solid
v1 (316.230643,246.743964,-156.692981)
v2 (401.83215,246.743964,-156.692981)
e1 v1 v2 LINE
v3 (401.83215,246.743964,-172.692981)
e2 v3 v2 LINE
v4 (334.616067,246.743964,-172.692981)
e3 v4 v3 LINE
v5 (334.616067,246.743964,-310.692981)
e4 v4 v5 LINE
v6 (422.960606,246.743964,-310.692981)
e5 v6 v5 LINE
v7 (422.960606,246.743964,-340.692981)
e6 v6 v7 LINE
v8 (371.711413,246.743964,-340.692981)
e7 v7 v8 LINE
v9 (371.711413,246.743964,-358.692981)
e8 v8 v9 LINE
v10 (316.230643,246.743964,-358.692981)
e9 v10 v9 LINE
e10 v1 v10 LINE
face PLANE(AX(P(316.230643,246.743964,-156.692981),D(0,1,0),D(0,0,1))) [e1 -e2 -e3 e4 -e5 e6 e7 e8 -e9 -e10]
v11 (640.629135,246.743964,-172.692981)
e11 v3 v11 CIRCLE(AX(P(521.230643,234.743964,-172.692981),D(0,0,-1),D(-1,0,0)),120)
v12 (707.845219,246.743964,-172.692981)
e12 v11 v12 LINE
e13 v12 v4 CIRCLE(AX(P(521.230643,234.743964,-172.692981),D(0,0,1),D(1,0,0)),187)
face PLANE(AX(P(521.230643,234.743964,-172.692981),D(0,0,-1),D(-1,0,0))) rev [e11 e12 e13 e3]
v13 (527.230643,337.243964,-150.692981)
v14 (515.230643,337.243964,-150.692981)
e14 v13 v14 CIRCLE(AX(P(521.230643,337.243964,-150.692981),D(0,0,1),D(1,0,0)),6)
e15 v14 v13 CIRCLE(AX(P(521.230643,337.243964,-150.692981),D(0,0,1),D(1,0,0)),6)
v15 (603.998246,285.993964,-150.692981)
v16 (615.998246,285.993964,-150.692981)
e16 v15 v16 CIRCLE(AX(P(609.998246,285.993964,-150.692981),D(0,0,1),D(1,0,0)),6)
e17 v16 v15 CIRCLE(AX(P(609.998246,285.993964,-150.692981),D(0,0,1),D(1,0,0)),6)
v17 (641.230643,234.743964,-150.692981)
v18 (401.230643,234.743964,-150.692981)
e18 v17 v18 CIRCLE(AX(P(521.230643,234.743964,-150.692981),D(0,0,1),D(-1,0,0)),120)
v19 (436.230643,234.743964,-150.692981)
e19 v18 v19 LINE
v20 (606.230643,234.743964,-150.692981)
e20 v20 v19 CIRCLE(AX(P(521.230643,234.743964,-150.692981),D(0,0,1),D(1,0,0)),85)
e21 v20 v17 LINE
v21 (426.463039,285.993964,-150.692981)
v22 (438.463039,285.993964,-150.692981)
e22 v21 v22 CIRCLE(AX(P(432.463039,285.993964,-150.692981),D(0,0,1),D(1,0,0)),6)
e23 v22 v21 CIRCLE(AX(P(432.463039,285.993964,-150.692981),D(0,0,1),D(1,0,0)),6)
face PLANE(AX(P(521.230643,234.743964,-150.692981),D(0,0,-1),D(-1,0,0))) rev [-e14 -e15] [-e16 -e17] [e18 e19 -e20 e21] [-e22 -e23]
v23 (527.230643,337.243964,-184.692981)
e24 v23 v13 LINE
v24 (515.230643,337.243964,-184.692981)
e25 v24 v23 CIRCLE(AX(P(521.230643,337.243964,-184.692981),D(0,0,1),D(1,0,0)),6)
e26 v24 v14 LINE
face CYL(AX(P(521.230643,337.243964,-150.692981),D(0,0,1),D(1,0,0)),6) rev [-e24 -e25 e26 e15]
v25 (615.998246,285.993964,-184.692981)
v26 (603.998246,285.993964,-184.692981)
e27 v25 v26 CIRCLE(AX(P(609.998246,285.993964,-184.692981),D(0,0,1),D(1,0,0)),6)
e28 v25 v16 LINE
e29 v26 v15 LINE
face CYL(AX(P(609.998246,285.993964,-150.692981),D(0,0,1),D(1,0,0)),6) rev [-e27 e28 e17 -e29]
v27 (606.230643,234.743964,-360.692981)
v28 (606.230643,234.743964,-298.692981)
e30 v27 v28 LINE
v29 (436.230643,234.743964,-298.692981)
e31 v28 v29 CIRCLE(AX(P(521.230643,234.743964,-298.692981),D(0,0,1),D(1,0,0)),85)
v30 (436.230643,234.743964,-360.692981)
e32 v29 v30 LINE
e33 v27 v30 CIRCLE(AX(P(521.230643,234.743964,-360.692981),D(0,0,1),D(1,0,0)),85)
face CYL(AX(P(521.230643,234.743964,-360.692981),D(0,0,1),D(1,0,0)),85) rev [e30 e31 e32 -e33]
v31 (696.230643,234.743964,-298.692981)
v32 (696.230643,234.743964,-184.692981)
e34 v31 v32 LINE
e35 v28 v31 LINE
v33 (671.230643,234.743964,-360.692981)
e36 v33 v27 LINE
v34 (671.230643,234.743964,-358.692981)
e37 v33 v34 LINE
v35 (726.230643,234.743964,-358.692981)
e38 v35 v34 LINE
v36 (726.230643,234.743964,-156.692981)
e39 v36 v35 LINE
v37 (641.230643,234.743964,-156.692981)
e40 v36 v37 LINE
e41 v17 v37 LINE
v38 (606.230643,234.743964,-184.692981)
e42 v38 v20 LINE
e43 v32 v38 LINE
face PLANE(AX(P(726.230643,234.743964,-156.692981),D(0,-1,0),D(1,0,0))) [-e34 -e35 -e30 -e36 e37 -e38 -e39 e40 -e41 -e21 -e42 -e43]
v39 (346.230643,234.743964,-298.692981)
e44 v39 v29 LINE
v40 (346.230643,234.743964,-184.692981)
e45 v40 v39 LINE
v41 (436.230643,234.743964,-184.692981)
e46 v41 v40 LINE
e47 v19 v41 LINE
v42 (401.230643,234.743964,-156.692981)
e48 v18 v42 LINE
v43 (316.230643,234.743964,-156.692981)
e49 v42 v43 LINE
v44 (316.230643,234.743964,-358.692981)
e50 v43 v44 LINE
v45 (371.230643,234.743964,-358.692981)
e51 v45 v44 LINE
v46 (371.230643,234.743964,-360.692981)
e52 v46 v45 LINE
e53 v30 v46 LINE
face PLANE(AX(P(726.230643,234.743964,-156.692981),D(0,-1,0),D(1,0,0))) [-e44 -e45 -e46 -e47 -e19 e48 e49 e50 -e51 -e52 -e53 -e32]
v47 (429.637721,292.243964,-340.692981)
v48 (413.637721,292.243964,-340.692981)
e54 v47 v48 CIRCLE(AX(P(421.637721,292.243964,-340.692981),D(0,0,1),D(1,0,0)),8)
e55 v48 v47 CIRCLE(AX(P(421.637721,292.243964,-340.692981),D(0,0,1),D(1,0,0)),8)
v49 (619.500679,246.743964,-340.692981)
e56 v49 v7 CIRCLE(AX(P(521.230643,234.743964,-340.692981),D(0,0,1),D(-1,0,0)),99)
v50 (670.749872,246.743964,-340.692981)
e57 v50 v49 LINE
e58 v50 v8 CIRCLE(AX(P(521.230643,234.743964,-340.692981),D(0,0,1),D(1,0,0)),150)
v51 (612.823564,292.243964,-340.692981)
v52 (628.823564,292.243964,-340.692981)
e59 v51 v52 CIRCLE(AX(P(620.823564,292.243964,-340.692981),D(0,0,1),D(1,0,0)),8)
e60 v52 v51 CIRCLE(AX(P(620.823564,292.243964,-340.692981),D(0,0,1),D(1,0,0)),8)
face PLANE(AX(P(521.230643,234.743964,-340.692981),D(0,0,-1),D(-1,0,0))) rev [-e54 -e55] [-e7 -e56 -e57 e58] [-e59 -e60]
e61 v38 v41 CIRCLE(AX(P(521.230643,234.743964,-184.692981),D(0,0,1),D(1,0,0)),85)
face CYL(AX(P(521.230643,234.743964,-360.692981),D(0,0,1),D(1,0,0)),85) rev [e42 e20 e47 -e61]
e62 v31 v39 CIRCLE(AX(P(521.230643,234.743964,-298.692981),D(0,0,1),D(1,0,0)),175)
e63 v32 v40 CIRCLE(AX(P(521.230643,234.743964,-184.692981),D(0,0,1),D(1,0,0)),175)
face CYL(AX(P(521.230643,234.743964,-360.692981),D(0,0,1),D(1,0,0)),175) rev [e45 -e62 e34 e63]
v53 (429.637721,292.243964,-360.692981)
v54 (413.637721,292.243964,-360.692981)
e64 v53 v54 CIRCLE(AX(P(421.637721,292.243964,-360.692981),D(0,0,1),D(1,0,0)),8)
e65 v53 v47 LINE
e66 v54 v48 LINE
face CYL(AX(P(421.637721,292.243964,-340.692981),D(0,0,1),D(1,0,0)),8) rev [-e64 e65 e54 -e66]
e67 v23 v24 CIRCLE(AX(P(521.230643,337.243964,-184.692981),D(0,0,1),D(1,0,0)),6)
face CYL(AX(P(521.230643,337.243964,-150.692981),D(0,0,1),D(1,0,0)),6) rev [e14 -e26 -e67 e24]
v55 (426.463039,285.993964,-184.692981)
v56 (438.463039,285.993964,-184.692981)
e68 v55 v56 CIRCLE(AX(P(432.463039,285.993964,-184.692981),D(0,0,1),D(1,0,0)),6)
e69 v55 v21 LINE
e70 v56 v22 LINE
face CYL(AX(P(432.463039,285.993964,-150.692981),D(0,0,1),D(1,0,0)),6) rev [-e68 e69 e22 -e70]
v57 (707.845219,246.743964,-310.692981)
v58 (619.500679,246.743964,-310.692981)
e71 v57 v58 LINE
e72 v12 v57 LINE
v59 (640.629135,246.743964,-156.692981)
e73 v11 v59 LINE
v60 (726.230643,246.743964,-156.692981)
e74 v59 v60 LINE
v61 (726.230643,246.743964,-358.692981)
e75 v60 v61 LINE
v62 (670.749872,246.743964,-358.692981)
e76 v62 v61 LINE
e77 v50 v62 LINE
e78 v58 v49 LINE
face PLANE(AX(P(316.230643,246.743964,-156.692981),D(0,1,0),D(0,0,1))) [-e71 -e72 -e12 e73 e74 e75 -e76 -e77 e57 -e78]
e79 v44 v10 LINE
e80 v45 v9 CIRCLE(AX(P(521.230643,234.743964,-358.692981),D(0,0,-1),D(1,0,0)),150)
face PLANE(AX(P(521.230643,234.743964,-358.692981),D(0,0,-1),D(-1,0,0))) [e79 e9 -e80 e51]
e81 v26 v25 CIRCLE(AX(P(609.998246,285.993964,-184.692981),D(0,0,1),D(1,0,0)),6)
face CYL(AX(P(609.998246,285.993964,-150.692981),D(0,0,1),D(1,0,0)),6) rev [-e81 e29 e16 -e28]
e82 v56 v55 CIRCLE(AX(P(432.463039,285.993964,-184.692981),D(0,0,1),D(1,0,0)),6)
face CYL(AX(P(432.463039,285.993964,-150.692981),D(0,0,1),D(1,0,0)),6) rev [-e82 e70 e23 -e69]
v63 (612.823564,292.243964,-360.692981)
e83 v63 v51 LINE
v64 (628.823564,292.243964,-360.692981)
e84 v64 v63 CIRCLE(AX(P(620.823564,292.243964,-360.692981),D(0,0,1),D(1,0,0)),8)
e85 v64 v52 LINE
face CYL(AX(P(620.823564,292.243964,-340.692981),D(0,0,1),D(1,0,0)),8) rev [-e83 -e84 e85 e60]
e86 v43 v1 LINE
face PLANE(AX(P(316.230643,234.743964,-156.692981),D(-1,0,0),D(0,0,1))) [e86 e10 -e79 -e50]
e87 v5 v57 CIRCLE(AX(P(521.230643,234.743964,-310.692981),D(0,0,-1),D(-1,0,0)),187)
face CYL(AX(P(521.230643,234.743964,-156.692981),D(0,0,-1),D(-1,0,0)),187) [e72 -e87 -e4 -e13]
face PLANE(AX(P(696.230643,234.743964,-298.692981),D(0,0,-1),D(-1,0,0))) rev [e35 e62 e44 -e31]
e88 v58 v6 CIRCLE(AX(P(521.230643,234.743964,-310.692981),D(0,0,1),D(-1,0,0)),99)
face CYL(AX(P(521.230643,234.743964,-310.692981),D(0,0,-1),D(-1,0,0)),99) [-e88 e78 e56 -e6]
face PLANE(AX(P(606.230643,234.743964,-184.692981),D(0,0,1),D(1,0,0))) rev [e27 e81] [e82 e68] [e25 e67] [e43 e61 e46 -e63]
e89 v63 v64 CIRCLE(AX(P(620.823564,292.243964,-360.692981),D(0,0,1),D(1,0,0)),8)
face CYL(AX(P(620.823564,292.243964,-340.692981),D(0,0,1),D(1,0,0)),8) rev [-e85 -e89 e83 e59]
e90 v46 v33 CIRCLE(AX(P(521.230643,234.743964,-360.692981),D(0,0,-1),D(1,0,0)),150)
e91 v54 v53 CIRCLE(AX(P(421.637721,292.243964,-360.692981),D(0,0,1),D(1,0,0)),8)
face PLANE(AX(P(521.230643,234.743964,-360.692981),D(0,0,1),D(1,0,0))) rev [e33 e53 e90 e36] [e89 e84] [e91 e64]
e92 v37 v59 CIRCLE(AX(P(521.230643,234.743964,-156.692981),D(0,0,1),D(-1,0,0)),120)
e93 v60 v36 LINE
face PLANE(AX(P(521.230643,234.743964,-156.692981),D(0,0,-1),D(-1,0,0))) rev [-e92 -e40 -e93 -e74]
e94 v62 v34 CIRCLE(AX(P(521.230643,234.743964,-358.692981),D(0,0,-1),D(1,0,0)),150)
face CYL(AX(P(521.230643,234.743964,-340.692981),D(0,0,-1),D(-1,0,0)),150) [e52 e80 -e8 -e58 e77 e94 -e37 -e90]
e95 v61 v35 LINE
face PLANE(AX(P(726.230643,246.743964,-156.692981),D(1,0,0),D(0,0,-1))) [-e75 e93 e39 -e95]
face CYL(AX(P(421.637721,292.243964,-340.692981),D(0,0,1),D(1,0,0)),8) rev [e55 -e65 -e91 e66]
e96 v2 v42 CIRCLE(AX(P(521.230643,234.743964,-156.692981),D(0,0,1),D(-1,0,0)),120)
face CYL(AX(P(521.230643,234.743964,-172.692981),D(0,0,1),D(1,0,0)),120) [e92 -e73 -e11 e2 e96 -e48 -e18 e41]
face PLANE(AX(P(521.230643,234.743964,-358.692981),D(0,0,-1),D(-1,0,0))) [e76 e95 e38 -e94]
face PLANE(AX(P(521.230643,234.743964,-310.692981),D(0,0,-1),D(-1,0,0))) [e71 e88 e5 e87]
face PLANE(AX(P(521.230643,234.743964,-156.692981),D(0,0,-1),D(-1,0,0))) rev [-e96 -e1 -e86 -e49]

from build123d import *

# Parameters (mm, degrees)
BOSS_EXTRUDE1_DEPTH            = 202
CUT_EXTRUDE1_START             = -16
CUT_EXTRUDE1_DEPTH             = 16
CUT_EXTRUDE2_DEPTH             = 18
CUT_EXTRUDE3_DEPTH             = 30
BOSS_EXTRUDE2_START            = 2
BOSS_EXTRUDE2_DEPTH            = 2
BOSS_EXTRUDE3_DEPTH            = 6
BOSS_EXTRUDE4_DEPTH            = 30
F_16_0_16_DIAMETER_HOLE1_D     = 16
F_16_0_16_DIAMETER_HOLE1_DEPTH = 20
F_12_0_12_DIAMETER_HOLE1_D     = 12
F_12_0_12_DIAMETER_HOLE1_DEPTH = 34


with BuildPart() as part:
    # Sketch1 → Boss-Extrude1 (new body)
    with BuildSketch(Plane(origin=(0, 0, -358.692981355), x_dir=(-1, 0, 0), z_dir=(0, 0, -1))):
        with BuildLine():
            Line((-707.84521865, 246.743963655), (-726.230642584, 246.743963655))
            Line((-726.230642584, 246.743963655), (-726.230642584, 234.743963655))
            Line((-726.230642584, 234.743963655), (-316.230642584, 234.743963655))
            Line((-316.230642584, 234.743963655), (-316.230642584, 246.743963655))
            Line((-316.230642584, 246.743963655), (-334.616066519, 246.743963655))
            ThreePointArc((-334.616066519, 246.743963655), (-521.230642584, 421.743963655), (-707.84521865, 246.743963655))
        make_face()
    extrude(amount=-BOSS_EXTRUDE1_DEPTH)

    # Sketch2 → Cut-Extrude1 (cut)
    with BuildSketch(Plane.XY.offset(-156.692981355).offset(CUT_EXTRUDE1_START)):
        with BuildLine():
            Line((640.629135037, 246.743963655), (707.84521865, 246.743963655))
            ThreePointArc((707.84521865, 246.743963655), (521.230642584, 421.743963655), (334.616066519, 246.743963655))
            Line((334.616066519, 246.743963655), (401.832150132, 246.743963655))
            ThreePointArc((401.832150132, 246.743963655), (521.230642584, 354.743963655), (640.629135037, 246.743963655))
        make_face()
    extrude(amount=CUT_EXTRUDE1_DEPTH, mode=Mode.SUBTRACT)

    # Sketch3 → Cut-Extrude2 (cut)
    with BuildSketch(Plane(origin=(0, 0, -358.692981355), x_dir=(-1, 0, 0), z_dir=(0, 0, -1))):
        with BuildLine():
            Line((-371.711413052, 246.743963655), (-334.616066519, 246.743963655))
            ThreePointArc((-334.616066519, 246.743963655), (-521.230642584, 421.743963654), (-707.84521865, 246.743963655))
            Line((-707.84521865, 246.743963655), (-670.749872117, 246.743963655))
            ThreePointArc((-670.749872117, 246.743963655), (-521.230642584, 384.743963654), (-371.711413052, 246.743963655))
        make_face()
    extrude(amount=-CUT_EXTRUDE2_DEPTH, mode=Mode.SUBTRACT)

    # Sketch4 → Cut-Extrude3 (cut)
    with BuildSketch(Plane(origin=(0, 0, -340.692981355), x_dir=(-1, 0, 0), z_dir=(0, 0, -1))):
        with BuildLine():
            Line((-707.84521865, 246.743963655), (-334.616066519, 246.743963655))
            ThreePointArc((-334.616066519, 246.743963655), (-521.230642584, 421.743963655), (-707.84521865, 246.743963655))
        make_face()
    extrude(amount=-CUT_EXTRUDE3_DEPTH, mode=Mode.SUBTRACT)

    # Sketch5 → Boss-Extrude2 (add)
    with BuildSketch(Plane(origin=(0, 0, -358.692981355), x_dir=(-1, 0, 0), z_dir=(0, 0, -1)).offset(BOSS_EXTRUDE2_START)):
        with BuildLine():
            Line((-371.230642584, 234.743963655), (-671.230642584, 234.743963655))
            ThreePointArc((-671.230642584, 234.743963655), (-521.230642584, 384.743963655), (-371.230642584, 234.743963655))
        make_face()
    extrude(amount=-BOSS_EXTRUDE2_DEPTH)

    # Sketch6 → Boss-Extrude3 (add)
    with BuildSketch(Plane.XY.offset(-156.692981355)):
        with BuildLine():
            Line((641.230642584, 234.743963655), (401.230642584, 234.743963655))
            ThreePointArc((401.230642584, 234.743963655), (521.230642584, 354.743963655), (641.230642584, 234.743963655))
        make_face()
    extrude(amount=BOSS_EXTRUDE3_DEPTH)

    # Sketch7 → Boss-Extrude4 (add)
    with BuildSketch(Plane.XY.offset(-340.692981355)):
        with BuildLine():
            Line((619.500678709, 246.743963655), (422.960606459, 246.743963655))
            ThreePointArc((422.960606459, 246.743963655), (521.230642584, 333.743963655), (619.500678709, 246.743963655))
        make_face()
    extrude(amount=BOSS_EXTRUDE4_DEPTH)

    # Sketch8 → Cut-Revolve1 (revolve, cut)
    with BuildSketch(Plane(origin=(0, 234.743963655, 0), x_dir=(1, 0, 0), z_dir=(0, 1, 0))):
        Polygon((606.230642584, 360.692981355), (521.230642584, 360.692981355), (521.230642584, 150.692981355), (606.230642584, 150.692981355), (606.230642584, 184.692981355), (696.230642584, 184.692981355), (696.230642584, 298.692981355), (606.230642584, 298.692981355), align=None)
    revolve(axis=Axis((521.230642584, 234.743963655, -360.692981355), (0, 0, 1)), mode=Mode.SUBTRACT)

    # Ø16.0 (16) diameter hole1
    with Locations(Plane.XY.offset(-340.692981355)):
        with Locations((421.637721149, 292.243963655), (620.82356402, 292.243963655)):
            Hole(F_16_0_16_DIAMETER_HOLE1_D / 2, depth=F_16_0_16_DIAMETER_HOLE1_DEPTH)

    # Ø12.0 (12) diameter hole1
    with Locations(Plane.XY.offset(-150.692981355)):
        with Locations((521.230642584, 337.243963655), (432.463038696, 285.993963655), (609.998246472, 285.993963655)):
            Hole(F_12_0_12_DIAMETER_HOLE1_D / 2, depth=F_12_0_12_DIAMETER_HOLE1_DEPTH)


solid = part.part
